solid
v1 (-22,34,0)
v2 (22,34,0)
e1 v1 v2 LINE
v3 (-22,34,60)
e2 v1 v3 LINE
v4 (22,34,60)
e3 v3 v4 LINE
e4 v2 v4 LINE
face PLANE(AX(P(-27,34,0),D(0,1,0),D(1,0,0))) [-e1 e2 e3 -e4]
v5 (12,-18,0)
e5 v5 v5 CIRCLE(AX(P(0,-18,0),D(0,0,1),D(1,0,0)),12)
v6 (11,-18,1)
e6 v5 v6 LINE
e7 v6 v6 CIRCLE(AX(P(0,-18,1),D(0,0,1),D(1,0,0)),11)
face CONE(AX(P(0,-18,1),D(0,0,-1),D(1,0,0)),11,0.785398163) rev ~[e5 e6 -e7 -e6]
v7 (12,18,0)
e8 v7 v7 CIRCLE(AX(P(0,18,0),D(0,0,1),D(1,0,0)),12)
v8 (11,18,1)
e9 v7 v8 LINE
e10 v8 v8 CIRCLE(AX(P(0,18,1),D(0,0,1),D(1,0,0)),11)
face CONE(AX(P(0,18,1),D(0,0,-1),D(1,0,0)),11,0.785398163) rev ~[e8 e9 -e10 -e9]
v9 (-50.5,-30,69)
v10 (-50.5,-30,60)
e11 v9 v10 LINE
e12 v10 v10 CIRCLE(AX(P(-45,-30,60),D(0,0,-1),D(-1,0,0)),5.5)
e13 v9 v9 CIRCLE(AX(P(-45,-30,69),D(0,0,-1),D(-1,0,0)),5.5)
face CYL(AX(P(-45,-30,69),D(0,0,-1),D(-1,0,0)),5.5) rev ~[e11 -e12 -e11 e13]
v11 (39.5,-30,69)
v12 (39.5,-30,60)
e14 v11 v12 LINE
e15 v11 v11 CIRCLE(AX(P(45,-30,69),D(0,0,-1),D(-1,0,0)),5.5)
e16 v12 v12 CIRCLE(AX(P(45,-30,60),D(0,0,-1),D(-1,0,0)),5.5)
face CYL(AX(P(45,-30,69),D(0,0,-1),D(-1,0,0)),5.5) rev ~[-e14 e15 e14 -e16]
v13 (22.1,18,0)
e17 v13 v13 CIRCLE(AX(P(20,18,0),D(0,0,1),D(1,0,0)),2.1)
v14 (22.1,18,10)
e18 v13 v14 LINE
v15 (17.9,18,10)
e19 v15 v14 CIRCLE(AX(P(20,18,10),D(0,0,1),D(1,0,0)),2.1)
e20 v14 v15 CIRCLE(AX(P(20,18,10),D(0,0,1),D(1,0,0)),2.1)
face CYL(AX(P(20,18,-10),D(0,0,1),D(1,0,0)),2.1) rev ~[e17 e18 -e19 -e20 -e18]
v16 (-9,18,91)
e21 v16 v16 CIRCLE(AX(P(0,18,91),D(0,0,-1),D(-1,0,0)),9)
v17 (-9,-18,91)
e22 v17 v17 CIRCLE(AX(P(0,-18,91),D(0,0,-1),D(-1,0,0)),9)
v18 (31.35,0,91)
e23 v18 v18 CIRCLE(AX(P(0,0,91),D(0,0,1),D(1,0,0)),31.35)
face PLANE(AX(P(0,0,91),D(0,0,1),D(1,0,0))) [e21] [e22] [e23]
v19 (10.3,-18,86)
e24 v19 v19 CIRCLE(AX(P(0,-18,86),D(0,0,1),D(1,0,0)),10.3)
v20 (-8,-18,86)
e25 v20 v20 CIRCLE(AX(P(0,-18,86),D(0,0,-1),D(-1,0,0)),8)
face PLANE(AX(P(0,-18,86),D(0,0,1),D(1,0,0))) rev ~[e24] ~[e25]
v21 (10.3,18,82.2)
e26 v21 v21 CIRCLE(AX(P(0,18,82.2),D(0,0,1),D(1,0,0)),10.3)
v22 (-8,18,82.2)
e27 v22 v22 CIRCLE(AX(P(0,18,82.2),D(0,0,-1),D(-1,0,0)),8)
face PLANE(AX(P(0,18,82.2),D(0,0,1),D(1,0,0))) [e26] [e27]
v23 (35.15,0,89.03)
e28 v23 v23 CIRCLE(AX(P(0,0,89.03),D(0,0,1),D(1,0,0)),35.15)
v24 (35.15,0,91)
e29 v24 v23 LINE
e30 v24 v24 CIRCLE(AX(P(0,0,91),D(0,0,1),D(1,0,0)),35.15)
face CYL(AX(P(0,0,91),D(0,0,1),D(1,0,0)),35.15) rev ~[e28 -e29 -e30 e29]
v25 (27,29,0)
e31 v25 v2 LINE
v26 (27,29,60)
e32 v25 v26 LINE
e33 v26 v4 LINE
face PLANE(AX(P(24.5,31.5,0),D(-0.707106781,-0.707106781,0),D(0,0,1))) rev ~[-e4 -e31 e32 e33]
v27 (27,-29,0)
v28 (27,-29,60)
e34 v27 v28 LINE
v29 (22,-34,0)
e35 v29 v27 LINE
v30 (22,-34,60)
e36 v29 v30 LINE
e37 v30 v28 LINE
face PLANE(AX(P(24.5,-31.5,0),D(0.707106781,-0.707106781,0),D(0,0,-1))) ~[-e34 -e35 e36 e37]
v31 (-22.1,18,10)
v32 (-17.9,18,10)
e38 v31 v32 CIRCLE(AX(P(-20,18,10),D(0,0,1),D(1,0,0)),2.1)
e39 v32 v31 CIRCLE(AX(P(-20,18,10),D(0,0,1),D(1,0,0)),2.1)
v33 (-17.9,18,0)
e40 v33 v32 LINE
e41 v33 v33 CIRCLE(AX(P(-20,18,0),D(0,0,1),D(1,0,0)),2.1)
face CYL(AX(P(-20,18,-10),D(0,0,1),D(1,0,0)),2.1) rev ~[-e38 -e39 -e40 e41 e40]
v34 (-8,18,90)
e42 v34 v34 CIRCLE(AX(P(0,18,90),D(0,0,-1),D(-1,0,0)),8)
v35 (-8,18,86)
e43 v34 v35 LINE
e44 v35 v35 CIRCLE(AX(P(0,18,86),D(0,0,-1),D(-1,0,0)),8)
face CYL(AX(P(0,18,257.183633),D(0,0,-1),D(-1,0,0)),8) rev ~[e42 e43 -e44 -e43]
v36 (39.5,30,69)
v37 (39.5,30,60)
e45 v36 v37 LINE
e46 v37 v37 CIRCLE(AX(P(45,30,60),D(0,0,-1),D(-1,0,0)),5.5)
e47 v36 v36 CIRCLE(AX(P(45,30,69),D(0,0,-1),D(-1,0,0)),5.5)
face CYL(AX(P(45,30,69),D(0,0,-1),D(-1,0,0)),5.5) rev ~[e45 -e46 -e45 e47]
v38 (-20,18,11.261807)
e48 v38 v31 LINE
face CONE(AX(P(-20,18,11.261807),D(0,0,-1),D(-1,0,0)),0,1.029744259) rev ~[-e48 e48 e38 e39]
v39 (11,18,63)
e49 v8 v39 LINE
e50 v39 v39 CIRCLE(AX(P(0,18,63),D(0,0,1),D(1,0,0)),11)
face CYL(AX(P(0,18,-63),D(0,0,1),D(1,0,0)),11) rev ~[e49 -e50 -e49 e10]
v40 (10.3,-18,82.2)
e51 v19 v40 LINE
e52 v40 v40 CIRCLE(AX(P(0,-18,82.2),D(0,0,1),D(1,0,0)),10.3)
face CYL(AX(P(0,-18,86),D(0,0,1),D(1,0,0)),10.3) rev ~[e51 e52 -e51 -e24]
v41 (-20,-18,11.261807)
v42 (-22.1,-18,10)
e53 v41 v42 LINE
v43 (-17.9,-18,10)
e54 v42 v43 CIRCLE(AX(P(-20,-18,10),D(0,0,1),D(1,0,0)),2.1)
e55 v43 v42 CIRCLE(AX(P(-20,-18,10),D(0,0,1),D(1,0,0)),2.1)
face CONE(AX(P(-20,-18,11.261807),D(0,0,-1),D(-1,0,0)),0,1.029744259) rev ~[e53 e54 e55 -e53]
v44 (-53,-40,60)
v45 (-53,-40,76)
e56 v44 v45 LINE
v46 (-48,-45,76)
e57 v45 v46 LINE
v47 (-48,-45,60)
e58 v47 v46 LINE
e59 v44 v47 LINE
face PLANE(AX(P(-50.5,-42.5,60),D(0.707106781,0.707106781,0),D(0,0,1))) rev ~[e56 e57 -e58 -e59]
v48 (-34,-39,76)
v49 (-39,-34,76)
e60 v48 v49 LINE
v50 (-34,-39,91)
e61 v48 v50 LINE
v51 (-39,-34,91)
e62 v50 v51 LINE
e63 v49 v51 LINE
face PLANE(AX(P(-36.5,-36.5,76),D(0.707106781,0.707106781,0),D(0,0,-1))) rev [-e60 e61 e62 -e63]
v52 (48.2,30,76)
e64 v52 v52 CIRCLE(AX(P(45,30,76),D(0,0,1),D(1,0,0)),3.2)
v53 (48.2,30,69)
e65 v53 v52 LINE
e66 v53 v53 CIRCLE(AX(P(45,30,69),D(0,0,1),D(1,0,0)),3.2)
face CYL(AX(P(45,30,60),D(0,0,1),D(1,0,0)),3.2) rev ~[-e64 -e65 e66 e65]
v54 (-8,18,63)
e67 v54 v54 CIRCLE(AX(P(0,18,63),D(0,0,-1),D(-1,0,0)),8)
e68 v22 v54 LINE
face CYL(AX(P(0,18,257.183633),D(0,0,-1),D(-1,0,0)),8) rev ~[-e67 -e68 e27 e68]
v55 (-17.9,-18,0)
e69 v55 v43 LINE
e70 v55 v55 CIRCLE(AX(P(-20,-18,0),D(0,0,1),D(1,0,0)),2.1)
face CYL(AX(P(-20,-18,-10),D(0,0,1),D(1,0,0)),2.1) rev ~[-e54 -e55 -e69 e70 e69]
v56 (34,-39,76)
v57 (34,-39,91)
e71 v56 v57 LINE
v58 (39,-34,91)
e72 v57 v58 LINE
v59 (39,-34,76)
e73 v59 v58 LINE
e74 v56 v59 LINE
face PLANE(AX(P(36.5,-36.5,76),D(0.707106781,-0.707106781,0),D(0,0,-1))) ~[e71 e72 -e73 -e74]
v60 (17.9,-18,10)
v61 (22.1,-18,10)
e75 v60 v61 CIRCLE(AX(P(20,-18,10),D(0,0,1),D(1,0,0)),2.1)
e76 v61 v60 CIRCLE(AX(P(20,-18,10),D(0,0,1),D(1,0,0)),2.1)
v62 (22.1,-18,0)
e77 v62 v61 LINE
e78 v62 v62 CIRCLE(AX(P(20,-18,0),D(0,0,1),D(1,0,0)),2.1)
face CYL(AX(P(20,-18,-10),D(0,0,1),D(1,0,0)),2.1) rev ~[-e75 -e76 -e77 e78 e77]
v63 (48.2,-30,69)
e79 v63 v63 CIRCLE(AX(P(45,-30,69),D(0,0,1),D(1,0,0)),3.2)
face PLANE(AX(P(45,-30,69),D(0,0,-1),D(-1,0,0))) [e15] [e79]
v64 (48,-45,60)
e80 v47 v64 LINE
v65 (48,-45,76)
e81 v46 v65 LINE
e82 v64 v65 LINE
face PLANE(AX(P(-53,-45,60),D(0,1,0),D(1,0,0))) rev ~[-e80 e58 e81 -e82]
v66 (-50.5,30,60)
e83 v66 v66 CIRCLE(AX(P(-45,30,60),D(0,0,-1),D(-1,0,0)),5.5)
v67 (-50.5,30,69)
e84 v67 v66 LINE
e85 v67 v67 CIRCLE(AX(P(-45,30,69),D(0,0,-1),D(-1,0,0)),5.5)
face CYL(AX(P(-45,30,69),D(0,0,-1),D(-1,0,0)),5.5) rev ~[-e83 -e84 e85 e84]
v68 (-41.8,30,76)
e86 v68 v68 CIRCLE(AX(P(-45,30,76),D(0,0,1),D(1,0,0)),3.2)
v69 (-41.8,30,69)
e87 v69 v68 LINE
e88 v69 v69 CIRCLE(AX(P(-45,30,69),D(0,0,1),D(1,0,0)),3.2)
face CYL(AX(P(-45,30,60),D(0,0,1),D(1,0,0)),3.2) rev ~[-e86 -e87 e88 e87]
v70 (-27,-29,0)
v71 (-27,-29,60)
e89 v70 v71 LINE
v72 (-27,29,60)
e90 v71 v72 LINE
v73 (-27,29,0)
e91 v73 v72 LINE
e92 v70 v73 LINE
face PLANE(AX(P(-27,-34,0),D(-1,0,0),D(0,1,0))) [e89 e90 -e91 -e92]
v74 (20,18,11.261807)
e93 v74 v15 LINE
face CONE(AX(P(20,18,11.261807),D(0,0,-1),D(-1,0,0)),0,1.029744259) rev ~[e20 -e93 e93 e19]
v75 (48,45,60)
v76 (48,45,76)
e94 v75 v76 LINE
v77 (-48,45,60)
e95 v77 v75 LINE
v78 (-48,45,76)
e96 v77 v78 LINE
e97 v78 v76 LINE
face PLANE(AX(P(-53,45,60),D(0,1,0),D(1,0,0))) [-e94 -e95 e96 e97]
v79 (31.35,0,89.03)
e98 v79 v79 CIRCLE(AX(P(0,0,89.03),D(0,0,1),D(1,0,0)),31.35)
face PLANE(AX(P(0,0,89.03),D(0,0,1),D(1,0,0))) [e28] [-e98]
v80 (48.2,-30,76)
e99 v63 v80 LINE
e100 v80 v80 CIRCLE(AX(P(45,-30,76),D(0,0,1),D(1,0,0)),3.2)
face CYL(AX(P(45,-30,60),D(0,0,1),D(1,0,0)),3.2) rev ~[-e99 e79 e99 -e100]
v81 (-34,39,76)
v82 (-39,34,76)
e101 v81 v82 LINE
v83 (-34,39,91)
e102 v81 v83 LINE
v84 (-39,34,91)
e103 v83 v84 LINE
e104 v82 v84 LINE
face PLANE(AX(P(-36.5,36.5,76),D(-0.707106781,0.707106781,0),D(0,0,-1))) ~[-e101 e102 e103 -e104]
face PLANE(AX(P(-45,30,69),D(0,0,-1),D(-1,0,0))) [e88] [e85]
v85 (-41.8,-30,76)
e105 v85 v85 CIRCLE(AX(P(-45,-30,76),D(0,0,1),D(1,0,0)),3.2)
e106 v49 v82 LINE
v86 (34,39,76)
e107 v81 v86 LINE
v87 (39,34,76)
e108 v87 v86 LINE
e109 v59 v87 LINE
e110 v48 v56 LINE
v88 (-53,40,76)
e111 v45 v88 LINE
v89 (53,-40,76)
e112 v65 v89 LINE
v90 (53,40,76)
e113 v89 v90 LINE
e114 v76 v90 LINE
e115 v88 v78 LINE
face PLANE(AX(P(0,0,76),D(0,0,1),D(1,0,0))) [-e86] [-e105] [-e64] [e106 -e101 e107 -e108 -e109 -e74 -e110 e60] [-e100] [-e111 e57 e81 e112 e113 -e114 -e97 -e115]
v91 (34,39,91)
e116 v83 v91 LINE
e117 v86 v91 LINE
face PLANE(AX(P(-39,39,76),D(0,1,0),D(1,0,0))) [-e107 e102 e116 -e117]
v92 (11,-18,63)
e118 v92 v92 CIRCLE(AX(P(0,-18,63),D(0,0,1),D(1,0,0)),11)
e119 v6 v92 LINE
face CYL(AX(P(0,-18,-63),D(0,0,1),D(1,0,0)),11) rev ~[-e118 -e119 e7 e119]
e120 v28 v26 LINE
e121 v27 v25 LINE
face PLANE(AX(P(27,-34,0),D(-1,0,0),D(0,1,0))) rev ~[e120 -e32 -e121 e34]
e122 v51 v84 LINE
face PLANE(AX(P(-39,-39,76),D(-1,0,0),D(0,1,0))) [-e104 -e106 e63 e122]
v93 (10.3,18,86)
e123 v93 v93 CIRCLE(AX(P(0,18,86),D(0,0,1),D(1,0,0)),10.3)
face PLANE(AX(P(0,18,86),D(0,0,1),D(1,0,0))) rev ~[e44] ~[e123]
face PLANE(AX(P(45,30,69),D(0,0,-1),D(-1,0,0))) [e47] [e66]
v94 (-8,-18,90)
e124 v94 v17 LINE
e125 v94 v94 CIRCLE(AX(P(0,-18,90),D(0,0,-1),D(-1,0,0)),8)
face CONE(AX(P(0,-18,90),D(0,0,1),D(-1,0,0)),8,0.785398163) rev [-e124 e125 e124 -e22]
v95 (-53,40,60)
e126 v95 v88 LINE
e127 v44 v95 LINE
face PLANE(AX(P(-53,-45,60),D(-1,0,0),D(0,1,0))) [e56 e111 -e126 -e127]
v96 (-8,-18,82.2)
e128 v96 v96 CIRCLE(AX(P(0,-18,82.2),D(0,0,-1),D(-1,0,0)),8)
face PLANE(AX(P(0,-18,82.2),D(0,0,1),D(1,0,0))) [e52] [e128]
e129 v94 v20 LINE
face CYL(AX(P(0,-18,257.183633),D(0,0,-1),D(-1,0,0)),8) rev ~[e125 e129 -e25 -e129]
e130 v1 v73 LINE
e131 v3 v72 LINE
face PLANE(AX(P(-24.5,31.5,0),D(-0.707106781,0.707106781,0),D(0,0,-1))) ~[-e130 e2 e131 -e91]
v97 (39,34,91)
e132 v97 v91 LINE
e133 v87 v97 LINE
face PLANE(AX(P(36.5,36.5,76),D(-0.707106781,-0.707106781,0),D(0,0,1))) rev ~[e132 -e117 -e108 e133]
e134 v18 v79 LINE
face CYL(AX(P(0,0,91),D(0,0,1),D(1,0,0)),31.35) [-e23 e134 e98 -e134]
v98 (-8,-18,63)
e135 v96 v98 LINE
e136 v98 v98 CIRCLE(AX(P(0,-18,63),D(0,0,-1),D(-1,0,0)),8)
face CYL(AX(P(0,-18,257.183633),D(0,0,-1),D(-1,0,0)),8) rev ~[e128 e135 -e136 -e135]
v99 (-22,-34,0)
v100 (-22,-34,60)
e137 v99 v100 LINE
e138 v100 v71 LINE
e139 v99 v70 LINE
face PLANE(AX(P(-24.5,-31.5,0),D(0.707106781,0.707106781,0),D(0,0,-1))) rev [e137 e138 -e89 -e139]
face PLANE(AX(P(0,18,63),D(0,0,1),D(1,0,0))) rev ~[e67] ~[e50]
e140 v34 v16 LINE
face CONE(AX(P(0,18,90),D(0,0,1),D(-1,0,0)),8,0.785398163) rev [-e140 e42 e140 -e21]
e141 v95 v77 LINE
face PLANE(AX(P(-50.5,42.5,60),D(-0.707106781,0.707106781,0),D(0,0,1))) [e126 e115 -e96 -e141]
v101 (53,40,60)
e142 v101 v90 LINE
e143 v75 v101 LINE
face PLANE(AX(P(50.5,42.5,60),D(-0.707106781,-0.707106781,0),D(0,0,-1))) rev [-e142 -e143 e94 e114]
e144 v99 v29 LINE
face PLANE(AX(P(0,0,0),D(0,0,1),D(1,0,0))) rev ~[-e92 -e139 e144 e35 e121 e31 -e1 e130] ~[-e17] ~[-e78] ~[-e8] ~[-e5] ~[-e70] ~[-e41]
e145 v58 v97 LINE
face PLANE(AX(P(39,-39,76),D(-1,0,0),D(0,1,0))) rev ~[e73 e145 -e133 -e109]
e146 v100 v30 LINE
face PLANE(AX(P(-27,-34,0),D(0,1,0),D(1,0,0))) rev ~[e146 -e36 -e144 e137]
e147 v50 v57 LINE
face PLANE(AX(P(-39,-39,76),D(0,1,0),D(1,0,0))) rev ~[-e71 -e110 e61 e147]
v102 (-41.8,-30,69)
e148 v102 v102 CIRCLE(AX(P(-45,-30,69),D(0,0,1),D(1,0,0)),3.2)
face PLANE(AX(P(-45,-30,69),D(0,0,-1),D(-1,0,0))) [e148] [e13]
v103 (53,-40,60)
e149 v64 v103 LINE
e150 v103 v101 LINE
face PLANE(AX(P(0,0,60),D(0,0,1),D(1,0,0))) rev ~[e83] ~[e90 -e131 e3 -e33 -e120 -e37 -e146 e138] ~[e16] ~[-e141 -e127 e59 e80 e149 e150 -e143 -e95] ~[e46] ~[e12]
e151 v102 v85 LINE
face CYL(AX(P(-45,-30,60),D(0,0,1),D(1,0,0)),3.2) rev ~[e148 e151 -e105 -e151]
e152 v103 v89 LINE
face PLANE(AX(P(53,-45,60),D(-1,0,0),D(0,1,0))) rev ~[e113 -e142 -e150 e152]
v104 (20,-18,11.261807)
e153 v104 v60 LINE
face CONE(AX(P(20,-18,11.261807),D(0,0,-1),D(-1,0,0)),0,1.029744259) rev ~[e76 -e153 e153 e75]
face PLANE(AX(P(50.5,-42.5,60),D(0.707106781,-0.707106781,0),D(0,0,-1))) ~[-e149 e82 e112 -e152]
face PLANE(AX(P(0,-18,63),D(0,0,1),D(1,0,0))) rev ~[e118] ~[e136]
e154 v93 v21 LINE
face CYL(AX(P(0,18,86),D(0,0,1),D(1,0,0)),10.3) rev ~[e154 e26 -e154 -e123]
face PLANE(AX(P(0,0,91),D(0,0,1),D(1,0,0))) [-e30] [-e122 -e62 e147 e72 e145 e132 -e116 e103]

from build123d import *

# Parameters (mm, degrees)
SKETCH1_W             = 54
SKETCH1_H             = 68
BOSS_EXTRUDE1_DEPTH   = 60
SKETCH2_W             = 106
SKETCH2_H             = 90
BOSS_EXTRUDE2_DEPTH   = 16
SKETCH3_W             = 78
SKETCH3_H             = 78
BOSS_EXTRUDE3_DEPTH   = 15
CHAMFER1_SIZE         = 5
SKETCH4_R             = 35.15
SKETCH4_R_2           = 31.35
CUT_EXTRUDE1_DEPTH    = 1.97
HOLE1_D               = 16
HOLE2_D               = 22
HOLE2_DEPTH           = 63
CHAMFER2_SIZE         = 1
M5_TAPPED_HOLE1_D     = 4.2
M5_TAPPED_HOLE1_DEPTH = 10
M5_TAPPED_HOLE1_TIP   = 1.2618073
HOLE3_D               = 6.4
HOLE3_CBORE_D         = 11
HOLE3_CBORE_DEPTH     = 9
SKETCH16_R            = 10.3
CUT_EXTRUDE2_DEPTH    = 3.8


with BuildPart() as part:
    # Sketch1 → Boss-Extrude1 (new body)
    with BuildSketch(Plane.XY):
        Rectangle(SKETCH1_W, SKETCH1_H)
    extrude(amount=BOSS_EXTRUDE1_DEPTH)

    # Sketch2 → Boss-Extrude2 (add)
    with BuildSketch(Plane.XY.offset(60)):
        Rectangle(SKETCH2_W, SKETCH2_H)
    extrude(amount=BOSS_EXTRUDE2_DEPTH)

    # Sketch3 → Boss-Extrude3 (add)
    with BuildSketch(Plane.XY.offset(76)):
        Rectangle(SKETCH3_W, SKETCH3_H)
    extrude(amount=BOSS_EXTRUDE3_DEPTH)

    # Chamfer1
    chamfer1_edges = [part.edges().sort_by_distance(p)[0] for p in [
        (-53, 45, 68),
        (-53, -45, 68),
        (53, -45, 68),
        (53, 45, 68),
        (-39, 39, 83.5),
        (-39, -39, 83.5),
        (39, -39, 83.5),
        (39, 39, 83.5),
        (27, -34, 30),
        (-27, -34, 30),
        (-27, 34, 30),
        (27, 34, 30),
    ]]
    chamfer(chamfer1_edges, length=CHAMFER1_SIZE)

    # Sketch4 → Cut-Extrude1 (cut)
    with BuildSketch(Plane.XY.offset(91)):
        Circle(SKETCH4_R)
        Circle(SKETCH4_R_2, mode=Mode.SUBTRACT)
    extrude(amount=-CUT_EXTRUDE1_DEPTH, mode=Mode.SUBTRACT)

    # Hole1 (through all)
    with Locations(Plane.XY.offset(91)):
        with Locations((0, -18), (0, 18)):
            Hole(HOLE1_D / 2)

    # Hole2
    with Locations(Plane(origin=(0, 0, 0), x_dir=(-1, 0, 0), z_dir=(0, 0, -1))):
        with Locations((0, 18), (0, -18)):
            Hole(HOLE2_D / 2, depth=HOLE2_DEPTH)

    # Chamfer2
    chamfer2_edges = [part.edges().sort_by_distance(p)[0] for p in [
        (8, 18, 91),
        (8, -18, 91),
        (-11, -18, 0),
        (-11, 18, 0),
    ]]
    chamfer(chamfer2_edges, length=CHAMFER2_SIZE)

    # M5 Tapped Hole1
    with Locations(Plane(origin=(0, 0, 0), x_dir=(-1, 0, 0), z_dir=(0, 0, -1))):
        with Locations((20, -18), (20, 18), (-20, 18), (-20, -18)):
            Hole(M5_TAPPED_HOLE1_D / 2, depth=M5_TAPPED_HOLE1_DEPTH)
            with Locations((0, 0, -(M5_TAPPED_HOLE1_DEPTH + M5_TAPPED_HOLE1_TIP / 2))):  # 118° drill point
                Cone(0, M5_TAPPED_HOLE1_D / 2, M5_TAPPED_HOLE1_TIP, mode=Mode.SUBTRACT)

    # Hole3 (through all)
    with Locations(Plane(origin=(0, 0, 60), x_dir=(-1, 0, 0), z_dir=(0, 0, -1))):
        with Locations((45, -30), (45, 30), (-45, 30), (-45, -30)):
            CounterBoreHole(HOLE3_D / 2, HOLE3_CBORE_D / 2, HOLE3_CBORE_DEPTH)

    # Sketch16 → Cut-Extrude2 (cut)
    with BuildSketch(Plane.XY.offset(86)):
        with Locations((0, 18)):
            Circle(SKETCH16_R)
        with Locations((0, -18)):
            Circle(SKETCH16_R)
    extrude(amount=-CUT_EXTRUDE2_DEPTH, mode=Mode.SUBTRACT)


solid = part.part
